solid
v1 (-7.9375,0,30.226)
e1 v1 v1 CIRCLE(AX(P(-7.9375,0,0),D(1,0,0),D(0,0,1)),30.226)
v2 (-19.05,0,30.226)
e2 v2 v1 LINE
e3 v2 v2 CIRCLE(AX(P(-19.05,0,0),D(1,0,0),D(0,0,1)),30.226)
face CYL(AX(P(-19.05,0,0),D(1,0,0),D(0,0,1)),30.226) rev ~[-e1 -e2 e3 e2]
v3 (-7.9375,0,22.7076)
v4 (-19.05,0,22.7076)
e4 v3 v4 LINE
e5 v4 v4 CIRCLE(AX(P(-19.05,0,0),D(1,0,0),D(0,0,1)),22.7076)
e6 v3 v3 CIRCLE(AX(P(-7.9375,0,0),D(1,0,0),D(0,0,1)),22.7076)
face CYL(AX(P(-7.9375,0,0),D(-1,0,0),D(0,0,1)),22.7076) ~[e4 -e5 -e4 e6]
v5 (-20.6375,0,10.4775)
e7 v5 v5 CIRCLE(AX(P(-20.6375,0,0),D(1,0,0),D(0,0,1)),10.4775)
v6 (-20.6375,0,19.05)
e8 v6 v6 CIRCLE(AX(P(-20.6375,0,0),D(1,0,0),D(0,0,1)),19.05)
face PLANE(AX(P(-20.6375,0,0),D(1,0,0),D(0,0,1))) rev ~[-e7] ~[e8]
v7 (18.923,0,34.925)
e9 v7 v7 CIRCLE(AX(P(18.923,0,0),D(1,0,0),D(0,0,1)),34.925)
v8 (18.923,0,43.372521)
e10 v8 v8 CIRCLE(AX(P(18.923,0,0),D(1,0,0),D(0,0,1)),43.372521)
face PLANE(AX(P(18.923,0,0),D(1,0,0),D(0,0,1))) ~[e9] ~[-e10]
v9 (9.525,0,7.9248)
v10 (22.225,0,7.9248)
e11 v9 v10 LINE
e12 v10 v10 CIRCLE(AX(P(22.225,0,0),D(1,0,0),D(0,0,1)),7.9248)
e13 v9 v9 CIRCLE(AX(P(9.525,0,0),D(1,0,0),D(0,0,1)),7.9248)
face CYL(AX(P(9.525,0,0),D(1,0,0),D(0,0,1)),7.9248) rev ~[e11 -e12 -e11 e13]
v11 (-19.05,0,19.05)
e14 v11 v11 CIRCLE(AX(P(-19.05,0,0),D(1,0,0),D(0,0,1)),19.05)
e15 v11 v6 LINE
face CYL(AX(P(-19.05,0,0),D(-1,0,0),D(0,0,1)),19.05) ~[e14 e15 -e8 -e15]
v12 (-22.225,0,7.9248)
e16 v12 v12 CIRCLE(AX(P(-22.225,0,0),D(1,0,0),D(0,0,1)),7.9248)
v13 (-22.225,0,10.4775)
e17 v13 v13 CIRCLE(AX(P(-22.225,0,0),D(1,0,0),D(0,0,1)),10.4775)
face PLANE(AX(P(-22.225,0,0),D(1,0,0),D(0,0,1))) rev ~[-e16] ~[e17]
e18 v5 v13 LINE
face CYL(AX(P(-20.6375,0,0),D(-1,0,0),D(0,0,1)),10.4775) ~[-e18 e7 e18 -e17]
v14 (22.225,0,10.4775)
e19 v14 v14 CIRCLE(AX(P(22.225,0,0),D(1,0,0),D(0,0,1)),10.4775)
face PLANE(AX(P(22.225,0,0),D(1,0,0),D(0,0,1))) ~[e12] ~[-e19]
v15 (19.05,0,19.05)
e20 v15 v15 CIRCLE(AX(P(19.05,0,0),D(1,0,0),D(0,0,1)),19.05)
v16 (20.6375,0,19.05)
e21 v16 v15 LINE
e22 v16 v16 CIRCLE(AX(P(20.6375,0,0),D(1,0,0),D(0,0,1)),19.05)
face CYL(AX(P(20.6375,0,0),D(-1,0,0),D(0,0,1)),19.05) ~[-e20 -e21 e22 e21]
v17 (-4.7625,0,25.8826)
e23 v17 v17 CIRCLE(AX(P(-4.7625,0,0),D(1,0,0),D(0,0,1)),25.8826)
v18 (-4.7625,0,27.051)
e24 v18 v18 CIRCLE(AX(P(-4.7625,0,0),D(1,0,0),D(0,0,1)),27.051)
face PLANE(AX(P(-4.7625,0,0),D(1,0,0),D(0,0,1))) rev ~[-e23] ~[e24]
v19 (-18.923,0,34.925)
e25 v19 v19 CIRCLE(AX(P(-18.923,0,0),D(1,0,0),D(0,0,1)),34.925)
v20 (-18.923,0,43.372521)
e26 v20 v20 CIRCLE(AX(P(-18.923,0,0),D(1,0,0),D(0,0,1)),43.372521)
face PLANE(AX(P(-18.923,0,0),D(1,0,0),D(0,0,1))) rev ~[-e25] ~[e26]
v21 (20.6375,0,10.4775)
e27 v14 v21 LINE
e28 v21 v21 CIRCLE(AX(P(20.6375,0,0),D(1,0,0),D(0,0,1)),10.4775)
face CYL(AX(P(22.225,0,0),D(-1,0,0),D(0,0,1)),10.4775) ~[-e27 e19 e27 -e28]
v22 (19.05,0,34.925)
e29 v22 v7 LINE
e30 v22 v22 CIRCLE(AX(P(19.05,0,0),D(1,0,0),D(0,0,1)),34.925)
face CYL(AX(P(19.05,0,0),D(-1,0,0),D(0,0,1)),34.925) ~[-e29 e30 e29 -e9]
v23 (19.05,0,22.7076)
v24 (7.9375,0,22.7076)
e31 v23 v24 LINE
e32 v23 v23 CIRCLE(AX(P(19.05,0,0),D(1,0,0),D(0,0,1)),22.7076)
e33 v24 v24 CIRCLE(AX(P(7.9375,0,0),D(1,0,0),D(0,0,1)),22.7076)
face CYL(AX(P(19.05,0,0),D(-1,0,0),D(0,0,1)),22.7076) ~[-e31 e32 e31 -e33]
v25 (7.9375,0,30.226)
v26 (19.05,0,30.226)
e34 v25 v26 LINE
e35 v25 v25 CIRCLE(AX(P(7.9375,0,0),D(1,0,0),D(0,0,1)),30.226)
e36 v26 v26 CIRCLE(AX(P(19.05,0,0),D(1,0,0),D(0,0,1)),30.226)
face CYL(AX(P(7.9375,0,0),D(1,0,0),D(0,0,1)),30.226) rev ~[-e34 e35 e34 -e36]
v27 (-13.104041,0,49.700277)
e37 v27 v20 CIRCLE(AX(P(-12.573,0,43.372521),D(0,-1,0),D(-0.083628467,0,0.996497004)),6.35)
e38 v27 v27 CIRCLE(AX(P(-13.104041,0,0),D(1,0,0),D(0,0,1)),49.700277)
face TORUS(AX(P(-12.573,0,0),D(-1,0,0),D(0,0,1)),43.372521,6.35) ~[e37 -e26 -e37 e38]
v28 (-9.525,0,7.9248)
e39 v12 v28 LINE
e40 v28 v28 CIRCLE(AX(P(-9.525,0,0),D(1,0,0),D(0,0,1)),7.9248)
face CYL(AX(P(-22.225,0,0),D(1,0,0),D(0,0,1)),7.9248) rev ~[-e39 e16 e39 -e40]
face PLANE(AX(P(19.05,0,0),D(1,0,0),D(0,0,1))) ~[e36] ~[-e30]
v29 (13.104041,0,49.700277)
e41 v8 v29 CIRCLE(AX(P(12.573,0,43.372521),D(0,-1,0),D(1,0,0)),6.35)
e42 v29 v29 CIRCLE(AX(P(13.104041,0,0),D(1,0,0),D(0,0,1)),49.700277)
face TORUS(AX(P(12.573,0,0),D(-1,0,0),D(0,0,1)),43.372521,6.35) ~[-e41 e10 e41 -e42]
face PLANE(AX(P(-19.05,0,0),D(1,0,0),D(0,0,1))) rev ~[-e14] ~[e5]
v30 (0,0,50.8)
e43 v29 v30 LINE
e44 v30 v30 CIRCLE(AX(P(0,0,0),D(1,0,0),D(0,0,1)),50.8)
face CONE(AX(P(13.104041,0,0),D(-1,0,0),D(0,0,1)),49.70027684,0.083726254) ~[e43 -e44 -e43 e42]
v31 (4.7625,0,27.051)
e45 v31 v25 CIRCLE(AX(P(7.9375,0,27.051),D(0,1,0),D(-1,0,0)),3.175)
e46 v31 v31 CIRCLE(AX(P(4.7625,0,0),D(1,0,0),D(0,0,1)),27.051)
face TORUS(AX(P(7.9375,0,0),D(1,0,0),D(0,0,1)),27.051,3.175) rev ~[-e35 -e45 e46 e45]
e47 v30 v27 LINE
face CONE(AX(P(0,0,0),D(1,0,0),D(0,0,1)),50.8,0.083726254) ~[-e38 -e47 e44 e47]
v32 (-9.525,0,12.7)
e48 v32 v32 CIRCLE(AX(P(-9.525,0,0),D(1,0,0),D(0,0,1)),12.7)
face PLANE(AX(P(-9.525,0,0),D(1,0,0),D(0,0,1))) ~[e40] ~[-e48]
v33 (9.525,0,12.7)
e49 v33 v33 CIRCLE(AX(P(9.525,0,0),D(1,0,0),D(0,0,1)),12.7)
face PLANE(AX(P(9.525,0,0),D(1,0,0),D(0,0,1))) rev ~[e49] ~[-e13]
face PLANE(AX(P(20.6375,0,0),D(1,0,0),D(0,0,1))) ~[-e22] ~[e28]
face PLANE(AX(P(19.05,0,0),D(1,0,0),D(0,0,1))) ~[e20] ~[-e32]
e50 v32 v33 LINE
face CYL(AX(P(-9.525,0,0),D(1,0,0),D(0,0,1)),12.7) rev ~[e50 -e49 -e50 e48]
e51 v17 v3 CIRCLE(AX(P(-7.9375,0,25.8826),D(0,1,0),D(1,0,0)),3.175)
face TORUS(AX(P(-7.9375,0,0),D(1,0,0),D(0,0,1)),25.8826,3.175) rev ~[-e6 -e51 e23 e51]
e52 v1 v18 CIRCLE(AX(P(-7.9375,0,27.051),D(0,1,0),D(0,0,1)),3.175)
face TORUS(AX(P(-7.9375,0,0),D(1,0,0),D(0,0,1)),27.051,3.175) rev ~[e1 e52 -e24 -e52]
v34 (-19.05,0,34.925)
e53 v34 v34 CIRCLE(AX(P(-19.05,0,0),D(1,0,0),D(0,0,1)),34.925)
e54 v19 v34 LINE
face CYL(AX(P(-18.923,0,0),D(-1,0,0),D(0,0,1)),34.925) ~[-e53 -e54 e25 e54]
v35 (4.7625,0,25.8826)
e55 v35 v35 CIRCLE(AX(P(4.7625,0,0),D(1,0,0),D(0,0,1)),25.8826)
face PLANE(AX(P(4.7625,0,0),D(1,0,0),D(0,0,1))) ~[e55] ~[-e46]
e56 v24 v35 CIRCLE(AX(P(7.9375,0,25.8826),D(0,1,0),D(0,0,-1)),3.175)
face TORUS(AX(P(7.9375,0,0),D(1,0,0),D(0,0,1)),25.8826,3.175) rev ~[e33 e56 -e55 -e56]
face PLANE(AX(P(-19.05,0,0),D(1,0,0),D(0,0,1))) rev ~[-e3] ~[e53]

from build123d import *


with BuildPart() as part:
    # Sketch3 → Revolve1 (revolve)
    with BuildSketch(Plane.XY, mode=Mode.PRIVATE) as revolve1_sk:
        with BuildLine():
            Line((-22.225, 7.9248), (-9.525, 7.9248))
            Line((-9.525, 7.9248), (-9.525, 12.7))
            Line((-9.525, 12.7), (9.525, 12.7))
            Line((9.525, 12.7), (9.525, 7.9248))
            Line((9.525, 7.9248), (22.225, 7.9248))
            Line((22.225, 7.9248), (22.225, 10.4775))
            Line((22.225, 10.4775), (20.6375, 10.4775))
            Line((20.6375, 10.4775), (20.6375, 19.05))
            Line((20.6375, 19.05), (19.05, 19.05))
            Line((19.05, 19.05), (19.05, 22.7076))
            Line((19.05, 22.7076), (7.9375, 22.7076))
            ThreePointArc((7.9375, 22.7076), (5.69243597, 23.63753597), (4.7625, 25.8826))
            Line((4.7625, 25.8826), (4.7625, 27.051))
            ThreePointArc((4.7625, 27.051), (5.69243597, 29.29606403), (7.9375, 30.226))
            Line((7.9375, 30.226), (19.05, 30.226))
            Line((19.05, 30.226), (19.05, 34.925))
            Line((19.05, 34.925), (18.923, 34.925))
            Line((18.923, 34.925), (18.923, 43.372520863))
            ThreePointArc((18.923, 43.372520863), (17.247110014, 47.670799073), (13.104040763, 49.70027684))
            Line((13.104040763, 49.70027684), (0, 50.8))
            Line((0, 50.8), (-13.104040763, 49.70027684))
            ThreePointArc((-13.104040763, 49.70027684), (-17.247110014, 47.670799073), (-18.923, 43.372520863))
            Line((-18.923, 43.372520863), (-18.923, 34.925))
            Line((-18.923, 34.925), (-19.05, 34.925))
            Line((-19.05, 34.925), (-19.05, 30.226))
            Line((-19.05, 30.226), (-7.9375, 30.226))
            ThreePointArc((-7.9375, 30.226), (-5.69243597, 29.29606403), (-4.7625, 27.051))
            Line((-4.7625, 27.051), (-4.7625, 25.8826))
            ThreePointArc((-4.7625, 25.8826), (-5.69243597, 23.63753597), (-7.9375, 22.7076))
            Line((-7.9375, 22.7076), (-19.05, 22.7076))
            Line((-19.05, 22.7076), (-19.05, 19.05))
            Line((-19.05, 19.05), (-20.6375, 19.05))
            Line((-20.6375, 19.05), (-20.6375, 10.4775))
            Line((-20.6375, 10.4775), (-22.225, 10.4775))
            Line((-22.225, 10.4775), (-22.225, 7.9248))
        make_face()
    revolve(revolve1_sk.sketch.rotate(Axis((-32.006619827, 0, 0), (1, 0, 0)), 90), axis=Axis((-32.006619827, 0, 0), (1, 0, 0)))


solid = part.part
